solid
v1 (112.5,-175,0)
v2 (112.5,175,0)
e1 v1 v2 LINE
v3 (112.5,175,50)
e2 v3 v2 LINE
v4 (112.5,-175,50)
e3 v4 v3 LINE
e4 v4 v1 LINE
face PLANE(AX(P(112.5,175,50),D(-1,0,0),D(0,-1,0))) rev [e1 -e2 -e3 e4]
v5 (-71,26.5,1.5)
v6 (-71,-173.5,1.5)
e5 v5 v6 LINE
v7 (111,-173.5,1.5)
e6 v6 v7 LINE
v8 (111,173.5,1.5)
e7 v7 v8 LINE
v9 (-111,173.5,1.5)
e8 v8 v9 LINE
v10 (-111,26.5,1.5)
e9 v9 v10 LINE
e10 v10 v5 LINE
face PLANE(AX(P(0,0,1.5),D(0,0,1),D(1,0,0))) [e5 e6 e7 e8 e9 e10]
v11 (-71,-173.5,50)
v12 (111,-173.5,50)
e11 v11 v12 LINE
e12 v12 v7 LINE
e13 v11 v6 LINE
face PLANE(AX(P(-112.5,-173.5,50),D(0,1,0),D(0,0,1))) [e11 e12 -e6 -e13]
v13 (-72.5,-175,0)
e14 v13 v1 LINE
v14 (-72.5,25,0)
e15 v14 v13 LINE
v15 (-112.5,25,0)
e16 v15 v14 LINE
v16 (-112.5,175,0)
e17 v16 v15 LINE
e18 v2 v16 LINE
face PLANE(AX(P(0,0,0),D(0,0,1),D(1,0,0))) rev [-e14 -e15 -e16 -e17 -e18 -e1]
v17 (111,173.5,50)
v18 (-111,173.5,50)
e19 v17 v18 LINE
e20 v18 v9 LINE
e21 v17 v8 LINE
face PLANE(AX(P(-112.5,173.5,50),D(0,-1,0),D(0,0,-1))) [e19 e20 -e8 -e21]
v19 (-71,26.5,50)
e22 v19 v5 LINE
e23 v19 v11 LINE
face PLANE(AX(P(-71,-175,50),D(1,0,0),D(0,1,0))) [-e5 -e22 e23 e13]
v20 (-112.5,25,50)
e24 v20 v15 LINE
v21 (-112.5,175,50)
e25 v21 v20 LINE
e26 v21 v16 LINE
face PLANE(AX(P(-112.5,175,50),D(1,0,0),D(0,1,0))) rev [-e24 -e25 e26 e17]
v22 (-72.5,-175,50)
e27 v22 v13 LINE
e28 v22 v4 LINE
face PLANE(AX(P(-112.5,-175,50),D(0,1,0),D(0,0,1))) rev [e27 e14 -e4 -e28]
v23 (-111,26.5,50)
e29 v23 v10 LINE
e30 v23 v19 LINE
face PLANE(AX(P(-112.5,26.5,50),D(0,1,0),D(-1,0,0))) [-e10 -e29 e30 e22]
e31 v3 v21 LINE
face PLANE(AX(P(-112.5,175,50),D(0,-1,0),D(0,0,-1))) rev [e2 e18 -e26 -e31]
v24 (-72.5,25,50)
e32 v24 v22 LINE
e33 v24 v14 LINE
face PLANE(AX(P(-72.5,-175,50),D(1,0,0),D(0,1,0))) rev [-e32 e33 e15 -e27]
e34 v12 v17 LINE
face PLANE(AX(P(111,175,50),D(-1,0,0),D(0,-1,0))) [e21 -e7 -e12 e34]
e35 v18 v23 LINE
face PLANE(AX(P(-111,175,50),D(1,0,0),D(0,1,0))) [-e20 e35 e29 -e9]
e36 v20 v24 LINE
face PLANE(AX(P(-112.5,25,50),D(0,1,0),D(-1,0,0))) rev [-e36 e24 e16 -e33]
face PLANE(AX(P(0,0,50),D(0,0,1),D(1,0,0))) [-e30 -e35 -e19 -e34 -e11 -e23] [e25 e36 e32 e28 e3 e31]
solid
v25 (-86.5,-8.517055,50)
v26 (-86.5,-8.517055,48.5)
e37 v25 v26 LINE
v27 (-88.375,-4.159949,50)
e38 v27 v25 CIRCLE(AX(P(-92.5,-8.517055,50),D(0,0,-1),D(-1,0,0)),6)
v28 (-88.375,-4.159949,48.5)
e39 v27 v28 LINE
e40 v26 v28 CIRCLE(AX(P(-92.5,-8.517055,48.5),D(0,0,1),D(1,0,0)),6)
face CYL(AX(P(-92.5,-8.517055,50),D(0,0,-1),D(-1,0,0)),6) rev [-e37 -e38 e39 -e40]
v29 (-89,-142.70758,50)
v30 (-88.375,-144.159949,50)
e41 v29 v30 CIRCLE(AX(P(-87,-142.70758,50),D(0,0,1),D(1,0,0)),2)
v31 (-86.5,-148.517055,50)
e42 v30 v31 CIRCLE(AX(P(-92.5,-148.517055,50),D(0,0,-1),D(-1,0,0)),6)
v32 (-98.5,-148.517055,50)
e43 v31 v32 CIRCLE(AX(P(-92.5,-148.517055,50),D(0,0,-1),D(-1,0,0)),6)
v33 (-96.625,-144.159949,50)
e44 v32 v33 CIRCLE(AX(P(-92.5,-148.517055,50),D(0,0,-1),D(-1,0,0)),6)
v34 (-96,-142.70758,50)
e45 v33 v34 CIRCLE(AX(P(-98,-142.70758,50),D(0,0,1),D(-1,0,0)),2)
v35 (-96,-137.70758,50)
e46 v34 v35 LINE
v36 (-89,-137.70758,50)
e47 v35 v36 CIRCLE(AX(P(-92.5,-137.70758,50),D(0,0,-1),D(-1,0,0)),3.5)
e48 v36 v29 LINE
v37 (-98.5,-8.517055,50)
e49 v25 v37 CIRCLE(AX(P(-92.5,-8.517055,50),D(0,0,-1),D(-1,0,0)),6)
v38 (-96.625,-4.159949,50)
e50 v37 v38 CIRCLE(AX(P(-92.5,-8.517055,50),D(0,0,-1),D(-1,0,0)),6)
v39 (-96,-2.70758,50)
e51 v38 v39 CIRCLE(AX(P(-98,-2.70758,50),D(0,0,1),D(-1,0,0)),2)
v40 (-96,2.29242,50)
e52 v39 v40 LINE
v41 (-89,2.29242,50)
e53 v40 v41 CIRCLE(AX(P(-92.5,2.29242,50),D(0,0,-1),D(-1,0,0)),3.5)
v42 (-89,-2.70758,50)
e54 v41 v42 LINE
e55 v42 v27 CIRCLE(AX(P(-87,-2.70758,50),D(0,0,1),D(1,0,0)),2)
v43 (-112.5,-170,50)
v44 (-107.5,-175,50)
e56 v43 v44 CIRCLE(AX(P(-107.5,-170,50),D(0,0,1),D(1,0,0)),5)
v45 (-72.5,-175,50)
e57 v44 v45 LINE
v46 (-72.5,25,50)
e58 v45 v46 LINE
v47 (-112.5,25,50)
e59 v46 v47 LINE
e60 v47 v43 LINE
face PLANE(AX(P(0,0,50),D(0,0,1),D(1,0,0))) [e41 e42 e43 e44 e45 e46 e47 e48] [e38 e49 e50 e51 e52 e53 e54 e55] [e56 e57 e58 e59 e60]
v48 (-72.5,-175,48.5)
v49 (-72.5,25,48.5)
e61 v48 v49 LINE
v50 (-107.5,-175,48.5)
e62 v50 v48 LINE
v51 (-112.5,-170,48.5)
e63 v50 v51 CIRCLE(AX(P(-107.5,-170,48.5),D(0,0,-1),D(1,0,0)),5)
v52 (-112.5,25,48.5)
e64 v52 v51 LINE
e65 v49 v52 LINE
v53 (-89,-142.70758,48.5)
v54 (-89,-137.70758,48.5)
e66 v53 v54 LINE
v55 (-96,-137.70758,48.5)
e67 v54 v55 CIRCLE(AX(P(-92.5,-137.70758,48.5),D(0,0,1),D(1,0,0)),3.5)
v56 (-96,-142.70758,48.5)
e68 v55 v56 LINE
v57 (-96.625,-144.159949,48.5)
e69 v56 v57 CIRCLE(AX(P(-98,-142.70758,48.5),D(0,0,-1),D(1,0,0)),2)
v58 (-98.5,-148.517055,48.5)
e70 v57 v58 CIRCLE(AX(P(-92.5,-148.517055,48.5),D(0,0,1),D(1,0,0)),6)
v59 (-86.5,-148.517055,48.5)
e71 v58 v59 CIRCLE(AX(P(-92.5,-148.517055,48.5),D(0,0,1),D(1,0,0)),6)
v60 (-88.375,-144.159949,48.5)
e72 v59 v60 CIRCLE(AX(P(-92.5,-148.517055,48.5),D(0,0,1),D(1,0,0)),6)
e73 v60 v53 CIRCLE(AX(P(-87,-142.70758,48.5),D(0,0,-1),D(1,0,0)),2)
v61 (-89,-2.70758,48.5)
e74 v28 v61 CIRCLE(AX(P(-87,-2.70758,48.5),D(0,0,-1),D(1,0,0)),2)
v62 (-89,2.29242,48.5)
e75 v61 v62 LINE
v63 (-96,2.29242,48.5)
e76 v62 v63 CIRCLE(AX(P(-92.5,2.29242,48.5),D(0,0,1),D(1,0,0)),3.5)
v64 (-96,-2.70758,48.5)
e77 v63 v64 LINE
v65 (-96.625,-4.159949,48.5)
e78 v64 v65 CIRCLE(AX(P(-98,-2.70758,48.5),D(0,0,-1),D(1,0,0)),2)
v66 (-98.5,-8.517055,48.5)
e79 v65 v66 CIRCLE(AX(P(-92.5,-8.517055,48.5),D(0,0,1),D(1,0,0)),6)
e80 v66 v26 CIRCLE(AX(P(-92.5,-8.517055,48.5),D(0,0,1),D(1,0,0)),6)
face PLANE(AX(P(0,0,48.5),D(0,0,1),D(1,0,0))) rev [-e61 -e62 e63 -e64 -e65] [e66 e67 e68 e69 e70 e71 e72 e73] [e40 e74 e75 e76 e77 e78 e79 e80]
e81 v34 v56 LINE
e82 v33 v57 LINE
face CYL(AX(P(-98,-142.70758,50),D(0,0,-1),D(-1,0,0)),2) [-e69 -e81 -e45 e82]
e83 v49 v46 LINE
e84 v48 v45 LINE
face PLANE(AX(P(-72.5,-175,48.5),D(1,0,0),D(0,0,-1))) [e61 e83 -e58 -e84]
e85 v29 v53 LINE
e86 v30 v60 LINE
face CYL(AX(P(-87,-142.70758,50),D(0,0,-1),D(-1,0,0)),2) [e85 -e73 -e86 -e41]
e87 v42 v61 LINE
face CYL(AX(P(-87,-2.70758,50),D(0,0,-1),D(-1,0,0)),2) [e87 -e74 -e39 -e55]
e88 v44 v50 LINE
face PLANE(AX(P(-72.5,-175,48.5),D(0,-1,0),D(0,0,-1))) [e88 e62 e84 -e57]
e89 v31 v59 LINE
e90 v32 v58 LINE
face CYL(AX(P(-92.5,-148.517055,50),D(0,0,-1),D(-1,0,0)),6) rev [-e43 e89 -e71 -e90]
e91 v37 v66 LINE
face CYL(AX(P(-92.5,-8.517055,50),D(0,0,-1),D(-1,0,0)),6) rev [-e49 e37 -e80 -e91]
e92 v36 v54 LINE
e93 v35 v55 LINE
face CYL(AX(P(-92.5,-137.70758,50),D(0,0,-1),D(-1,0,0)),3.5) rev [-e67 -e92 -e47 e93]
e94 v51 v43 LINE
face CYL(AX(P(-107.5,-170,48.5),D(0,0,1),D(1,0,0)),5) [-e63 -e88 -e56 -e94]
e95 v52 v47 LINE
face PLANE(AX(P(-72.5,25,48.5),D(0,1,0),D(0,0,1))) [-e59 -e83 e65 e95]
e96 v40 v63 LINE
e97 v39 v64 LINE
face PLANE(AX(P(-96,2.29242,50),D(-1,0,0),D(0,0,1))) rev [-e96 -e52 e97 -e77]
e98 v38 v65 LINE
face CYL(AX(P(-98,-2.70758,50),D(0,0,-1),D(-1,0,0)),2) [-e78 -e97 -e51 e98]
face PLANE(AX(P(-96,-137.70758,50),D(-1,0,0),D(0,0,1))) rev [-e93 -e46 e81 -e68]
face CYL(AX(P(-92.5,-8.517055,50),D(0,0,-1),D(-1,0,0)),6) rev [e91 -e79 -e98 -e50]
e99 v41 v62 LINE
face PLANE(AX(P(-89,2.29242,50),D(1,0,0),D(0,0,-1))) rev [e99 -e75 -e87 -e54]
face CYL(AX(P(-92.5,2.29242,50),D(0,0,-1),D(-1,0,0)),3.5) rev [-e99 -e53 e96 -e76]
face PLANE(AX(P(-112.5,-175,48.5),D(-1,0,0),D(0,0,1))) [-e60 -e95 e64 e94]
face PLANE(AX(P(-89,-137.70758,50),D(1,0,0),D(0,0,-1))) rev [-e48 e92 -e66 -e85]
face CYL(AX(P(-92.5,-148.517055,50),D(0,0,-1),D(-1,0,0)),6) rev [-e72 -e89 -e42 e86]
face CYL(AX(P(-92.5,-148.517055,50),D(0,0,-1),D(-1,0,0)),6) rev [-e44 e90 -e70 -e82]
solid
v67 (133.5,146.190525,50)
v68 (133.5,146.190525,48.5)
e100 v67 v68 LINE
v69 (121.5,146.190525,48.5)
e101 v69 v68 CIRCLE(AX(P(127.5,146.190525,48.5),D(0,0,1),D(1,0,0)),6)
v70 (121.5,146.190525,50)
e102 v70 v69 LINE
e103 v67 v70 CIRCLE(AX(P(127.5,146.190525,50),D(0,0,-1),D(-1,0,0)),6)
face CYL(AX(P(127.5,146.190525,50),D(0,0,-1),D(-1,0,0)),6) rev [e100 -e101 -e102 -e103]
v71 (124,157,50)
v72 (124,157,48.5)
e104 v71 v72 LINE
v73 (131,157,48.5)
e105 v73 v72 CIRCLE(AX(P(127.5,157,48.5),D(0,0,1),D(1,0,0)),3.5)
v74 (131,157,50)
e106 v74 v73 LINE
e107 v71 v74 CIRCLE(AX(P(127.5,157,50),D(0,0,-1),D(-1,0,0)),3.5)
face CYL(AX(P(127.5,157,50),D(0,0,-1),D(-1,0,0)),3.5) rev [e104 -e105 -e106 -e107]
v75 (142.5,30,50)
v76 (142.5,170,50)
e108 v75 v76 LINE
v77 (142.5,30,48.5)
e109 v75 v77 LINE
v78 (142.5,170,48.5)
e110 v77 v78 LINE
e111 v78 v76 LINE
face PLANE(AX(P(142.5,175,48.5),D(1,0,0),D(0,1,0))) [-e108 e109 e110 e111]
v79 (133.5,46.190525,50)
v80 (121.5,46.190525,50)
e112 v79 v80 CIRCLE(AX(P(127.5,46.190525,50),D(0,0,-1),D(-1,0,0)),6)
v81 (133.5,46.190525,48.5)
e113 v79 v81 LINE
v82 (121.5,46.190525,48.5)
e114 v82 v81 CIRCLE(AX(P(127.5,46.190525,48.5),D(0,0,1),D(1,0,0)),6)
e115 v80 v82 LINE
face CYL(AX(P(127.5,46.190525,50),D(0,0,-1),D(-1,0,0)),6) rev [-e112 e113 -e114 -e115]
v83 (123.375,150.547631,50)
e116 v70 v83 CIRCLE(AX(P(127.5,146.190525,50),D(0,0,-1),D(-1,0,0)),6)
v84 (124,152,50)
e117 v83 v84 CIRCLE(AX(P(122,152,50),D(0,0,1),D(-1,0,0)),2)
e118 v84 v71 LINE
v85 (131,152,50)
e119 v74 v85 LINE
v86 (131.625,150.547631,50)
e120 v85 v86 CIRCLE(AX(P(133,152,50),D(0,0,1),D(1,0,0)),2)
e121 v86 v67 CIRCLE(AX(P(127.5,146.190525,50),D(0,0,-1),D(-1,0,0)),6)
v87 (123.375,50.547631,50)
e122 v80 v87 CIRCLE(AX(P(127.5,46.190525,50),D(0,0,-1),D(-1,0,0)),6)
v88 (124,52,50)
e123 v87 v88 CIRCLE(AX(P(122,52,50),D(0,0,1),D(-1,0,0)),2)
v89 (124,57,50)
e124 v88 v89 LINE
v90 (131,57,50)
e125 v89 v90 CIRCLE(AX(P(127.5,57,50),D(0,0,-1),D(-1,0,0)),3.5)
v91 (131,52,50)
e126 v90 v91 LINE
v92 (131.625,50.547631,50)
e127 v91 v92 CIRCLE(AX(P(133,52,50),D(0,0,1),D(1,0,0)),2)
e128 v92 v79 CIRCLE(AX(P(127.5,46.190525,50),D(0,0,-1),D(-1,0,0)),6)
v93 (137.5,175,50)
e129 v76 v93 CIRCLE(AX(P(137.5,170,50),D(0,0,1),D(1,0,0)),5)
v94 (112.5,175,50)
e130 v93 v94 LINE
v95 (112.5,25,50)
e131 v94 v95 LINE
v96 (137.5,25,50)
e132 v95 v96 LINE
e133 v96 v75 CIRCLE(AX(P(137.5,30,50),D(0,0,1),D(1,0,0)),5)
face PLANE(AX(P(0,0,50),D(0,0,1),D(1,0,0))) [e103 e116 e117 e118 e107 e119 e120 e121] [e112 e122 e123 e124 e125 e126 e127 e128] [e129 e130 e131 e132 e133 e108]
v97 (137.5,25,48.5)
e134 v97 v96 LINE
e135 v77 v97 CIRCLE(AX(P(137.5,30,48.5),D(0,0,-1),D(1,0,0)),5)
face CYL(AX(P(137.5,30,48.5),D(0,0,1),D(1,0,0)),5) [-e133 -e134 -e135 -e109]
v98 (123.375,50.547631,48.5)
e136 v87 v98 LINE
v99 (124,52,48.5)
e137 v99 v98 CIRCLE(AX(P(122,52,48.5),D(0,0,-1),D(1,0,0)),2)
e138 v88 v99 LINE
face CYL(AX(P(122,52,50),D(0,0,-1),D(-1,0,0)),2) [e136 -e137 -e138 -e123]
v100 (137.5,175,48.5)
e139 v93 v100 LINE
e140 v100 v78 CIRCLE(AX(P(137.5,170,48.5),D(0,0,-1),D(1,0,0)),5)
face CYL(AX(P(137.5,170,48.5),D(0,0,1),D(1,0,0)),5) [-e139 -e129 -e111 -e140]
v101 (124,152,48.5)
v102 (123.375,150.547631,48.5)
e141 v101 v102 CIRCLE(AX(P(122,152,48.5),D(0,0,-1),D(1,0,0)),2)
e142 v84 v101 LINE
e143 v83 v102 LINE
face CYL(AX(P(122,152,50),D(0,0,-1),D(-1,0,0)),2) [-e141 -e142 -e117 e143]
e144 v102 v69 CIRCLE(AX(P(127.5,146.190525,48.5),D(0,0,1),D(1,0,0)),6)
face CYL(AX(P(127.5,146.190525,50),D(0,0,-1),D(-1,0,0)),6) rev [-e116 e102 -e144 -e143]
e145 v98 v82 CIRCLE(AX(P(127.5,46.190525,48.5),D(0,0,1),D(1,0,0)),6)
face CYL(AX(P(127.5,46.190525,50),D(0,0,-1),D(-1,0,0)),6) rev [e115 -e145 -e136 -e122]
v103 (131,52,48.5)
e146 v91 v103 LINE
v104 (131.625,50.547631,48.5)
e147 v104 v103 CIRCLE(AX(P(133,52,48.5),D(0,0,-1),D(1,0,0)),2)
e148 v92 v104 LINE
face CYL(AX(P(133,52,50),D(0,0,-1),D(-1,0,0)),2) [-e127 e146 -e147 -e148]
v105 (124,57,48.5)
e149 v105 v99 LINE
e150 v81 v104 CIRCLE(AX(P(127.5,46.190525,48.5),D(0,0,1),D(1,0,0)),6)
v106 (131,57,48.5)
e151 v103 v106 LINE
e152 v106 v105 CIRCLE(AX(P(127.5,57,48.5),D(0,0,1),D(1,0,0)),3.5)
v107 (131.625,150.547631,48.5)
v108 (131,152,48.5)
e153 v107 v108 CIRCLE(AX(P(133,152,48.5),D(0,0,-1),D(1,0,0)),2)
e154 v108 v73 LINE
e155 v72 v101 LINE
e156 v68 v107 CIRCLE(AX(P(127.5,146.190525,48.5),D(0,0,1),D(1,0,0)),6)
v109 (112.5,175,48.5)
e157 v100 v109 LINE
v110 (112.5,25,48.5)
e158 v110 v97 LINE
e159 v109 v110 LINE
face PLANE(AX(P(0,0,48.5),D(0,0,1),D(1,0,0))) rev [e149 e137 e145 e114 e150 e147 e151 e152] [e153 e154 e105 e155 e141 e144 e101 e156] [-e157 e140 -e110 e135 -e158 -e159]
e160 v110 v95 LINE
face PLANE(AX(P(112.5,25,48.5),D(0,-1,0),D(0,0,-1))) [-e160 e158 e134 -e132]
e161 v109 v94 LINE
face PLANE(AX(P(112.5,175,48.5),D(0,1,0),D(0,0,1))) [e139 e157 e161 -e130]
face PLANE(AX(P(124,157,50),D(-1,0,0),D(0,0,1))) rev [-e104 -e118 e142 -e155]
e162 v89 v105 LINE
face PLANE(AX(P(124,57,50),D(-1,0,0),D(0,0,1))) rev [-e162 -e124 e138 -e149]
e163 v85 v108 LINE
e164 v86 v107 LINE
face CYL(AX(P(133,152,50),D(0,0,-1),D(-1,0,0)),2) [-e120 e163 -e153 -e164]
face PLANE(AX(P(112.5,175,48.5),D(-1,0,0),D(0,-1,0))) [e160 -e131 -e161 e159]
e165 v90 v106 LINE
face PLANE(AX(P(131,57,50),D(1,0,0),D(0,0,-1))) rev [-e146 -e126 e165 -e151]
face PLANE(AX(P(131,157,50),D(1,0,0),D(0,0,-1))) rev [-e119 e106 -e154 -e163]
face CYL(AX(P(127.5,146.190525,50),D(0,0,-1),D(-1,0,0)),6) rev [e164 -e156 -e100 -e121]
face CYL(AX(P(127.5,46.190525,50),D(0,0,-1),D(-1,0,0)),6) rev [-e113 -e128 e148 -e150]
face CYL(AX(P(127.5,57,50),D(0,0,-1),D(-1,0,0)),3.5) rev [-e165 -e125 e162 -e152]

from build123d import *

# Parameters (mm, degrees)
SKETCH_1_W          = 225
SKETCH_1_H          = 350
EXTRUDE_1_DEPTH     = 50
SKETCH_2_W          = 40
SKETCH_2_H          = 200
CUT_EXTRUDE_1_DEPTH = 214.965534608
SHELL_1_T           = -1.5
SKETCH_3_W          = 40
SKETCH_3_H          = 200
EXTRUDE_2_DEPTH     = 1.5
SKETCH_3_W_2        = 30
SKETCH_3_H_2        = 150
EXTRUDE_2_2_DEPTH   = 1.5
FILLET_1_R          = 5
FILLET_2_R          = 5
CUT_EXTRUDE_4_DEPTH = 232.152006264


with BuildPart() as part:
    # 草图1 → 凸台-拉伸1 (new body)
    with BuildSketch(Plane.XY):
        Rectangle(SKETCH_1_W, SKETCH_1_H)
    extrude(amount=EXTRUDE_1_DEPTH)

    # 草图2 → 切除-拉伸1 (cut, through all)
    with BuildSketch(Plane(origin=(0, 0, 0), x_dir=(-1, 0, 0), z_dir=(0, 0, -1))):
        with Locations((92.5, -75)):
            Rectangle(SKETCH_2_W, SKETCH_2_H)
    extrude(amount=-CUT_EXTRUDE_1_DEPTH, mode=Mode.SUBTRACT)

    # 抽壳1
    shell_1_openings = [part.faces().sort_by_distance(p)[0] for p in [
        (10.459363958, 8.480565371, 50),
    ]]
    offset(amount=SHELL_1_T, openings=shell_1_openings, kind=Kind.INTERSECTION)


with BuildPart() as body_2:
    # 草图3 → 凸台-拉伸2 (new body)
    with BuildSketch(Plane.XY.offset(50)):
        with Locations((-92.5, -75)):
            Rectangle(SKETCH_3_W, SKETCH_3_H)
    extrude(amount=-EXTRUDE_2_DEPTH)

    # 圆角2
    fillet_2_edges = [body_2.edges().sort_by_distance(p)[0] for p in [
        (-112.5, -175, 49.25),
    ]]
    fillet(fillet_2_edges, radius=FILLET_2_R)


with BuildPart() as body_3:
    # 草图3 → Extrude 2 2 (new body)
    with BuildSketch(Plane.XY.offset(50)):
        with Locations((127.5, 100)):
            Rectangle(SKETCH_3_W_2, SKETCH_3_H_2)
    extrude(amount=-EXTRUDE_2_2_DEPTH)

    # 圆角1
    fillet_1_edges = [body_3.edges().sort_by_distance(p)[0] for p in [
        (142.5, 175, 49.25),
        (142.5, 25, 49.25),
    ]]
    fillet(fillet_1_edges, radius=FILLET_1_R)


with BuildPart() as cut_extrude_4_tool:
    # 草图4 → 切除-拉伸4 (new, through all)
    with BuildSketch(Plane(origin=(0, 0, 0), x_dir=(-1, 0, 0), z_dir=(0, 0, -1))):
        with BuildLine():
            Line((96, 2.292420126), (96, -2.707579874))
            ThreePointArc((96, -2.707579874), (96.162882693, -3.498149289), (96.625, -4.159948629))
            ThreePointArc((96.625, -4.159948629), (92.5, -14.517054893), (88.375, -4.159948629))
            ThreePointArc((88.375, -4.159948629), (88.837117307, -3.498149289), (89, -2.707579874))
            Line((89, -2.707579874), (89, 2.292420126))
            ThreePointArc((89, 2.292420126), (92.5, 5.792420126), (96, 2.292420126))
        make_face()
        with BuildLine():
            Line((96, -137.707579874), (96, -142.707579874))
            ThreePointArc((96, -142.707579874), (96.162882693, -143.498149289), (96.625, -144.159948629))
            ThreePointArc((96.625, -144.159948629), (92.5, -154.517054893), (88.375, -144.159948629))
            ThreePointArc((88.375, -144.159948629), (88.837117307, -143.498149289), (89, -142.707579874))
            Line((89, -142.707579874), (89, -137.707579874))
            ThreePointArc((89, -137.707579874), (92.5, -134.207579874), (96, -137.707579874))
        make_face()
        with BuildLine():
            Line((-124, 157), (-124, 152))
            ThreePointArc((-124, 152), (-123.837117307, 151.209430585), (-123.375, 150.547631245))
            ThreePointArc((-123.375, 150.547631245), (-127.5, 140.190524981), (-131.625, 150.547631245))
            ThreePointArc((-131.625, 150.547631245), (-131.162882693, 151.209430585), (-131, 152))
            Line((-131, 152), (-131, 157))
            ThreePointArc((-131, 157), (-127.5, 160.5), (-124, 157))
        make_face()
        with BuildLine():
            Line((-124, 57), (-124, 52))
            ThreePointArc((-124, 52), (-123.837117307, 51.209430585), (-123.375, 50.547631245))
            ThreePointArc((-123.375, 50.547631245), (-127.5, 40.190524981), (-131.625, 50.547631245))
            ThreePointArc((-131.625, 50.547631245), (-131.162882693, 51.209430585), (-131, 52))
            Line((-131, 52), (-131, 57))
            ThreePointArc((-131, 57), (-127.5, 60.5), (-124, 57))
        make_face()
    extrude(amount=-CUT_EXTRUDE_4_DEPTH)


with BuildPart() as body_2_1:
    add(body_2.part)

    # 切除-拉伸4: cut by cut_extrude_4_tool
    add(cut_extrude_4_tool.part, mode=Mode.SUBTRACT)


with BuildPart() as body_3_1:
    add(body_3.part)

    # 切除-拉伸4: cut by cut_extrude_4_tool
    add(cut_extrude_4_tool.part, mode=Mode.SUBTRACT)


solid = Compound([part.part, body_2_1.part, body_3_1.part])
